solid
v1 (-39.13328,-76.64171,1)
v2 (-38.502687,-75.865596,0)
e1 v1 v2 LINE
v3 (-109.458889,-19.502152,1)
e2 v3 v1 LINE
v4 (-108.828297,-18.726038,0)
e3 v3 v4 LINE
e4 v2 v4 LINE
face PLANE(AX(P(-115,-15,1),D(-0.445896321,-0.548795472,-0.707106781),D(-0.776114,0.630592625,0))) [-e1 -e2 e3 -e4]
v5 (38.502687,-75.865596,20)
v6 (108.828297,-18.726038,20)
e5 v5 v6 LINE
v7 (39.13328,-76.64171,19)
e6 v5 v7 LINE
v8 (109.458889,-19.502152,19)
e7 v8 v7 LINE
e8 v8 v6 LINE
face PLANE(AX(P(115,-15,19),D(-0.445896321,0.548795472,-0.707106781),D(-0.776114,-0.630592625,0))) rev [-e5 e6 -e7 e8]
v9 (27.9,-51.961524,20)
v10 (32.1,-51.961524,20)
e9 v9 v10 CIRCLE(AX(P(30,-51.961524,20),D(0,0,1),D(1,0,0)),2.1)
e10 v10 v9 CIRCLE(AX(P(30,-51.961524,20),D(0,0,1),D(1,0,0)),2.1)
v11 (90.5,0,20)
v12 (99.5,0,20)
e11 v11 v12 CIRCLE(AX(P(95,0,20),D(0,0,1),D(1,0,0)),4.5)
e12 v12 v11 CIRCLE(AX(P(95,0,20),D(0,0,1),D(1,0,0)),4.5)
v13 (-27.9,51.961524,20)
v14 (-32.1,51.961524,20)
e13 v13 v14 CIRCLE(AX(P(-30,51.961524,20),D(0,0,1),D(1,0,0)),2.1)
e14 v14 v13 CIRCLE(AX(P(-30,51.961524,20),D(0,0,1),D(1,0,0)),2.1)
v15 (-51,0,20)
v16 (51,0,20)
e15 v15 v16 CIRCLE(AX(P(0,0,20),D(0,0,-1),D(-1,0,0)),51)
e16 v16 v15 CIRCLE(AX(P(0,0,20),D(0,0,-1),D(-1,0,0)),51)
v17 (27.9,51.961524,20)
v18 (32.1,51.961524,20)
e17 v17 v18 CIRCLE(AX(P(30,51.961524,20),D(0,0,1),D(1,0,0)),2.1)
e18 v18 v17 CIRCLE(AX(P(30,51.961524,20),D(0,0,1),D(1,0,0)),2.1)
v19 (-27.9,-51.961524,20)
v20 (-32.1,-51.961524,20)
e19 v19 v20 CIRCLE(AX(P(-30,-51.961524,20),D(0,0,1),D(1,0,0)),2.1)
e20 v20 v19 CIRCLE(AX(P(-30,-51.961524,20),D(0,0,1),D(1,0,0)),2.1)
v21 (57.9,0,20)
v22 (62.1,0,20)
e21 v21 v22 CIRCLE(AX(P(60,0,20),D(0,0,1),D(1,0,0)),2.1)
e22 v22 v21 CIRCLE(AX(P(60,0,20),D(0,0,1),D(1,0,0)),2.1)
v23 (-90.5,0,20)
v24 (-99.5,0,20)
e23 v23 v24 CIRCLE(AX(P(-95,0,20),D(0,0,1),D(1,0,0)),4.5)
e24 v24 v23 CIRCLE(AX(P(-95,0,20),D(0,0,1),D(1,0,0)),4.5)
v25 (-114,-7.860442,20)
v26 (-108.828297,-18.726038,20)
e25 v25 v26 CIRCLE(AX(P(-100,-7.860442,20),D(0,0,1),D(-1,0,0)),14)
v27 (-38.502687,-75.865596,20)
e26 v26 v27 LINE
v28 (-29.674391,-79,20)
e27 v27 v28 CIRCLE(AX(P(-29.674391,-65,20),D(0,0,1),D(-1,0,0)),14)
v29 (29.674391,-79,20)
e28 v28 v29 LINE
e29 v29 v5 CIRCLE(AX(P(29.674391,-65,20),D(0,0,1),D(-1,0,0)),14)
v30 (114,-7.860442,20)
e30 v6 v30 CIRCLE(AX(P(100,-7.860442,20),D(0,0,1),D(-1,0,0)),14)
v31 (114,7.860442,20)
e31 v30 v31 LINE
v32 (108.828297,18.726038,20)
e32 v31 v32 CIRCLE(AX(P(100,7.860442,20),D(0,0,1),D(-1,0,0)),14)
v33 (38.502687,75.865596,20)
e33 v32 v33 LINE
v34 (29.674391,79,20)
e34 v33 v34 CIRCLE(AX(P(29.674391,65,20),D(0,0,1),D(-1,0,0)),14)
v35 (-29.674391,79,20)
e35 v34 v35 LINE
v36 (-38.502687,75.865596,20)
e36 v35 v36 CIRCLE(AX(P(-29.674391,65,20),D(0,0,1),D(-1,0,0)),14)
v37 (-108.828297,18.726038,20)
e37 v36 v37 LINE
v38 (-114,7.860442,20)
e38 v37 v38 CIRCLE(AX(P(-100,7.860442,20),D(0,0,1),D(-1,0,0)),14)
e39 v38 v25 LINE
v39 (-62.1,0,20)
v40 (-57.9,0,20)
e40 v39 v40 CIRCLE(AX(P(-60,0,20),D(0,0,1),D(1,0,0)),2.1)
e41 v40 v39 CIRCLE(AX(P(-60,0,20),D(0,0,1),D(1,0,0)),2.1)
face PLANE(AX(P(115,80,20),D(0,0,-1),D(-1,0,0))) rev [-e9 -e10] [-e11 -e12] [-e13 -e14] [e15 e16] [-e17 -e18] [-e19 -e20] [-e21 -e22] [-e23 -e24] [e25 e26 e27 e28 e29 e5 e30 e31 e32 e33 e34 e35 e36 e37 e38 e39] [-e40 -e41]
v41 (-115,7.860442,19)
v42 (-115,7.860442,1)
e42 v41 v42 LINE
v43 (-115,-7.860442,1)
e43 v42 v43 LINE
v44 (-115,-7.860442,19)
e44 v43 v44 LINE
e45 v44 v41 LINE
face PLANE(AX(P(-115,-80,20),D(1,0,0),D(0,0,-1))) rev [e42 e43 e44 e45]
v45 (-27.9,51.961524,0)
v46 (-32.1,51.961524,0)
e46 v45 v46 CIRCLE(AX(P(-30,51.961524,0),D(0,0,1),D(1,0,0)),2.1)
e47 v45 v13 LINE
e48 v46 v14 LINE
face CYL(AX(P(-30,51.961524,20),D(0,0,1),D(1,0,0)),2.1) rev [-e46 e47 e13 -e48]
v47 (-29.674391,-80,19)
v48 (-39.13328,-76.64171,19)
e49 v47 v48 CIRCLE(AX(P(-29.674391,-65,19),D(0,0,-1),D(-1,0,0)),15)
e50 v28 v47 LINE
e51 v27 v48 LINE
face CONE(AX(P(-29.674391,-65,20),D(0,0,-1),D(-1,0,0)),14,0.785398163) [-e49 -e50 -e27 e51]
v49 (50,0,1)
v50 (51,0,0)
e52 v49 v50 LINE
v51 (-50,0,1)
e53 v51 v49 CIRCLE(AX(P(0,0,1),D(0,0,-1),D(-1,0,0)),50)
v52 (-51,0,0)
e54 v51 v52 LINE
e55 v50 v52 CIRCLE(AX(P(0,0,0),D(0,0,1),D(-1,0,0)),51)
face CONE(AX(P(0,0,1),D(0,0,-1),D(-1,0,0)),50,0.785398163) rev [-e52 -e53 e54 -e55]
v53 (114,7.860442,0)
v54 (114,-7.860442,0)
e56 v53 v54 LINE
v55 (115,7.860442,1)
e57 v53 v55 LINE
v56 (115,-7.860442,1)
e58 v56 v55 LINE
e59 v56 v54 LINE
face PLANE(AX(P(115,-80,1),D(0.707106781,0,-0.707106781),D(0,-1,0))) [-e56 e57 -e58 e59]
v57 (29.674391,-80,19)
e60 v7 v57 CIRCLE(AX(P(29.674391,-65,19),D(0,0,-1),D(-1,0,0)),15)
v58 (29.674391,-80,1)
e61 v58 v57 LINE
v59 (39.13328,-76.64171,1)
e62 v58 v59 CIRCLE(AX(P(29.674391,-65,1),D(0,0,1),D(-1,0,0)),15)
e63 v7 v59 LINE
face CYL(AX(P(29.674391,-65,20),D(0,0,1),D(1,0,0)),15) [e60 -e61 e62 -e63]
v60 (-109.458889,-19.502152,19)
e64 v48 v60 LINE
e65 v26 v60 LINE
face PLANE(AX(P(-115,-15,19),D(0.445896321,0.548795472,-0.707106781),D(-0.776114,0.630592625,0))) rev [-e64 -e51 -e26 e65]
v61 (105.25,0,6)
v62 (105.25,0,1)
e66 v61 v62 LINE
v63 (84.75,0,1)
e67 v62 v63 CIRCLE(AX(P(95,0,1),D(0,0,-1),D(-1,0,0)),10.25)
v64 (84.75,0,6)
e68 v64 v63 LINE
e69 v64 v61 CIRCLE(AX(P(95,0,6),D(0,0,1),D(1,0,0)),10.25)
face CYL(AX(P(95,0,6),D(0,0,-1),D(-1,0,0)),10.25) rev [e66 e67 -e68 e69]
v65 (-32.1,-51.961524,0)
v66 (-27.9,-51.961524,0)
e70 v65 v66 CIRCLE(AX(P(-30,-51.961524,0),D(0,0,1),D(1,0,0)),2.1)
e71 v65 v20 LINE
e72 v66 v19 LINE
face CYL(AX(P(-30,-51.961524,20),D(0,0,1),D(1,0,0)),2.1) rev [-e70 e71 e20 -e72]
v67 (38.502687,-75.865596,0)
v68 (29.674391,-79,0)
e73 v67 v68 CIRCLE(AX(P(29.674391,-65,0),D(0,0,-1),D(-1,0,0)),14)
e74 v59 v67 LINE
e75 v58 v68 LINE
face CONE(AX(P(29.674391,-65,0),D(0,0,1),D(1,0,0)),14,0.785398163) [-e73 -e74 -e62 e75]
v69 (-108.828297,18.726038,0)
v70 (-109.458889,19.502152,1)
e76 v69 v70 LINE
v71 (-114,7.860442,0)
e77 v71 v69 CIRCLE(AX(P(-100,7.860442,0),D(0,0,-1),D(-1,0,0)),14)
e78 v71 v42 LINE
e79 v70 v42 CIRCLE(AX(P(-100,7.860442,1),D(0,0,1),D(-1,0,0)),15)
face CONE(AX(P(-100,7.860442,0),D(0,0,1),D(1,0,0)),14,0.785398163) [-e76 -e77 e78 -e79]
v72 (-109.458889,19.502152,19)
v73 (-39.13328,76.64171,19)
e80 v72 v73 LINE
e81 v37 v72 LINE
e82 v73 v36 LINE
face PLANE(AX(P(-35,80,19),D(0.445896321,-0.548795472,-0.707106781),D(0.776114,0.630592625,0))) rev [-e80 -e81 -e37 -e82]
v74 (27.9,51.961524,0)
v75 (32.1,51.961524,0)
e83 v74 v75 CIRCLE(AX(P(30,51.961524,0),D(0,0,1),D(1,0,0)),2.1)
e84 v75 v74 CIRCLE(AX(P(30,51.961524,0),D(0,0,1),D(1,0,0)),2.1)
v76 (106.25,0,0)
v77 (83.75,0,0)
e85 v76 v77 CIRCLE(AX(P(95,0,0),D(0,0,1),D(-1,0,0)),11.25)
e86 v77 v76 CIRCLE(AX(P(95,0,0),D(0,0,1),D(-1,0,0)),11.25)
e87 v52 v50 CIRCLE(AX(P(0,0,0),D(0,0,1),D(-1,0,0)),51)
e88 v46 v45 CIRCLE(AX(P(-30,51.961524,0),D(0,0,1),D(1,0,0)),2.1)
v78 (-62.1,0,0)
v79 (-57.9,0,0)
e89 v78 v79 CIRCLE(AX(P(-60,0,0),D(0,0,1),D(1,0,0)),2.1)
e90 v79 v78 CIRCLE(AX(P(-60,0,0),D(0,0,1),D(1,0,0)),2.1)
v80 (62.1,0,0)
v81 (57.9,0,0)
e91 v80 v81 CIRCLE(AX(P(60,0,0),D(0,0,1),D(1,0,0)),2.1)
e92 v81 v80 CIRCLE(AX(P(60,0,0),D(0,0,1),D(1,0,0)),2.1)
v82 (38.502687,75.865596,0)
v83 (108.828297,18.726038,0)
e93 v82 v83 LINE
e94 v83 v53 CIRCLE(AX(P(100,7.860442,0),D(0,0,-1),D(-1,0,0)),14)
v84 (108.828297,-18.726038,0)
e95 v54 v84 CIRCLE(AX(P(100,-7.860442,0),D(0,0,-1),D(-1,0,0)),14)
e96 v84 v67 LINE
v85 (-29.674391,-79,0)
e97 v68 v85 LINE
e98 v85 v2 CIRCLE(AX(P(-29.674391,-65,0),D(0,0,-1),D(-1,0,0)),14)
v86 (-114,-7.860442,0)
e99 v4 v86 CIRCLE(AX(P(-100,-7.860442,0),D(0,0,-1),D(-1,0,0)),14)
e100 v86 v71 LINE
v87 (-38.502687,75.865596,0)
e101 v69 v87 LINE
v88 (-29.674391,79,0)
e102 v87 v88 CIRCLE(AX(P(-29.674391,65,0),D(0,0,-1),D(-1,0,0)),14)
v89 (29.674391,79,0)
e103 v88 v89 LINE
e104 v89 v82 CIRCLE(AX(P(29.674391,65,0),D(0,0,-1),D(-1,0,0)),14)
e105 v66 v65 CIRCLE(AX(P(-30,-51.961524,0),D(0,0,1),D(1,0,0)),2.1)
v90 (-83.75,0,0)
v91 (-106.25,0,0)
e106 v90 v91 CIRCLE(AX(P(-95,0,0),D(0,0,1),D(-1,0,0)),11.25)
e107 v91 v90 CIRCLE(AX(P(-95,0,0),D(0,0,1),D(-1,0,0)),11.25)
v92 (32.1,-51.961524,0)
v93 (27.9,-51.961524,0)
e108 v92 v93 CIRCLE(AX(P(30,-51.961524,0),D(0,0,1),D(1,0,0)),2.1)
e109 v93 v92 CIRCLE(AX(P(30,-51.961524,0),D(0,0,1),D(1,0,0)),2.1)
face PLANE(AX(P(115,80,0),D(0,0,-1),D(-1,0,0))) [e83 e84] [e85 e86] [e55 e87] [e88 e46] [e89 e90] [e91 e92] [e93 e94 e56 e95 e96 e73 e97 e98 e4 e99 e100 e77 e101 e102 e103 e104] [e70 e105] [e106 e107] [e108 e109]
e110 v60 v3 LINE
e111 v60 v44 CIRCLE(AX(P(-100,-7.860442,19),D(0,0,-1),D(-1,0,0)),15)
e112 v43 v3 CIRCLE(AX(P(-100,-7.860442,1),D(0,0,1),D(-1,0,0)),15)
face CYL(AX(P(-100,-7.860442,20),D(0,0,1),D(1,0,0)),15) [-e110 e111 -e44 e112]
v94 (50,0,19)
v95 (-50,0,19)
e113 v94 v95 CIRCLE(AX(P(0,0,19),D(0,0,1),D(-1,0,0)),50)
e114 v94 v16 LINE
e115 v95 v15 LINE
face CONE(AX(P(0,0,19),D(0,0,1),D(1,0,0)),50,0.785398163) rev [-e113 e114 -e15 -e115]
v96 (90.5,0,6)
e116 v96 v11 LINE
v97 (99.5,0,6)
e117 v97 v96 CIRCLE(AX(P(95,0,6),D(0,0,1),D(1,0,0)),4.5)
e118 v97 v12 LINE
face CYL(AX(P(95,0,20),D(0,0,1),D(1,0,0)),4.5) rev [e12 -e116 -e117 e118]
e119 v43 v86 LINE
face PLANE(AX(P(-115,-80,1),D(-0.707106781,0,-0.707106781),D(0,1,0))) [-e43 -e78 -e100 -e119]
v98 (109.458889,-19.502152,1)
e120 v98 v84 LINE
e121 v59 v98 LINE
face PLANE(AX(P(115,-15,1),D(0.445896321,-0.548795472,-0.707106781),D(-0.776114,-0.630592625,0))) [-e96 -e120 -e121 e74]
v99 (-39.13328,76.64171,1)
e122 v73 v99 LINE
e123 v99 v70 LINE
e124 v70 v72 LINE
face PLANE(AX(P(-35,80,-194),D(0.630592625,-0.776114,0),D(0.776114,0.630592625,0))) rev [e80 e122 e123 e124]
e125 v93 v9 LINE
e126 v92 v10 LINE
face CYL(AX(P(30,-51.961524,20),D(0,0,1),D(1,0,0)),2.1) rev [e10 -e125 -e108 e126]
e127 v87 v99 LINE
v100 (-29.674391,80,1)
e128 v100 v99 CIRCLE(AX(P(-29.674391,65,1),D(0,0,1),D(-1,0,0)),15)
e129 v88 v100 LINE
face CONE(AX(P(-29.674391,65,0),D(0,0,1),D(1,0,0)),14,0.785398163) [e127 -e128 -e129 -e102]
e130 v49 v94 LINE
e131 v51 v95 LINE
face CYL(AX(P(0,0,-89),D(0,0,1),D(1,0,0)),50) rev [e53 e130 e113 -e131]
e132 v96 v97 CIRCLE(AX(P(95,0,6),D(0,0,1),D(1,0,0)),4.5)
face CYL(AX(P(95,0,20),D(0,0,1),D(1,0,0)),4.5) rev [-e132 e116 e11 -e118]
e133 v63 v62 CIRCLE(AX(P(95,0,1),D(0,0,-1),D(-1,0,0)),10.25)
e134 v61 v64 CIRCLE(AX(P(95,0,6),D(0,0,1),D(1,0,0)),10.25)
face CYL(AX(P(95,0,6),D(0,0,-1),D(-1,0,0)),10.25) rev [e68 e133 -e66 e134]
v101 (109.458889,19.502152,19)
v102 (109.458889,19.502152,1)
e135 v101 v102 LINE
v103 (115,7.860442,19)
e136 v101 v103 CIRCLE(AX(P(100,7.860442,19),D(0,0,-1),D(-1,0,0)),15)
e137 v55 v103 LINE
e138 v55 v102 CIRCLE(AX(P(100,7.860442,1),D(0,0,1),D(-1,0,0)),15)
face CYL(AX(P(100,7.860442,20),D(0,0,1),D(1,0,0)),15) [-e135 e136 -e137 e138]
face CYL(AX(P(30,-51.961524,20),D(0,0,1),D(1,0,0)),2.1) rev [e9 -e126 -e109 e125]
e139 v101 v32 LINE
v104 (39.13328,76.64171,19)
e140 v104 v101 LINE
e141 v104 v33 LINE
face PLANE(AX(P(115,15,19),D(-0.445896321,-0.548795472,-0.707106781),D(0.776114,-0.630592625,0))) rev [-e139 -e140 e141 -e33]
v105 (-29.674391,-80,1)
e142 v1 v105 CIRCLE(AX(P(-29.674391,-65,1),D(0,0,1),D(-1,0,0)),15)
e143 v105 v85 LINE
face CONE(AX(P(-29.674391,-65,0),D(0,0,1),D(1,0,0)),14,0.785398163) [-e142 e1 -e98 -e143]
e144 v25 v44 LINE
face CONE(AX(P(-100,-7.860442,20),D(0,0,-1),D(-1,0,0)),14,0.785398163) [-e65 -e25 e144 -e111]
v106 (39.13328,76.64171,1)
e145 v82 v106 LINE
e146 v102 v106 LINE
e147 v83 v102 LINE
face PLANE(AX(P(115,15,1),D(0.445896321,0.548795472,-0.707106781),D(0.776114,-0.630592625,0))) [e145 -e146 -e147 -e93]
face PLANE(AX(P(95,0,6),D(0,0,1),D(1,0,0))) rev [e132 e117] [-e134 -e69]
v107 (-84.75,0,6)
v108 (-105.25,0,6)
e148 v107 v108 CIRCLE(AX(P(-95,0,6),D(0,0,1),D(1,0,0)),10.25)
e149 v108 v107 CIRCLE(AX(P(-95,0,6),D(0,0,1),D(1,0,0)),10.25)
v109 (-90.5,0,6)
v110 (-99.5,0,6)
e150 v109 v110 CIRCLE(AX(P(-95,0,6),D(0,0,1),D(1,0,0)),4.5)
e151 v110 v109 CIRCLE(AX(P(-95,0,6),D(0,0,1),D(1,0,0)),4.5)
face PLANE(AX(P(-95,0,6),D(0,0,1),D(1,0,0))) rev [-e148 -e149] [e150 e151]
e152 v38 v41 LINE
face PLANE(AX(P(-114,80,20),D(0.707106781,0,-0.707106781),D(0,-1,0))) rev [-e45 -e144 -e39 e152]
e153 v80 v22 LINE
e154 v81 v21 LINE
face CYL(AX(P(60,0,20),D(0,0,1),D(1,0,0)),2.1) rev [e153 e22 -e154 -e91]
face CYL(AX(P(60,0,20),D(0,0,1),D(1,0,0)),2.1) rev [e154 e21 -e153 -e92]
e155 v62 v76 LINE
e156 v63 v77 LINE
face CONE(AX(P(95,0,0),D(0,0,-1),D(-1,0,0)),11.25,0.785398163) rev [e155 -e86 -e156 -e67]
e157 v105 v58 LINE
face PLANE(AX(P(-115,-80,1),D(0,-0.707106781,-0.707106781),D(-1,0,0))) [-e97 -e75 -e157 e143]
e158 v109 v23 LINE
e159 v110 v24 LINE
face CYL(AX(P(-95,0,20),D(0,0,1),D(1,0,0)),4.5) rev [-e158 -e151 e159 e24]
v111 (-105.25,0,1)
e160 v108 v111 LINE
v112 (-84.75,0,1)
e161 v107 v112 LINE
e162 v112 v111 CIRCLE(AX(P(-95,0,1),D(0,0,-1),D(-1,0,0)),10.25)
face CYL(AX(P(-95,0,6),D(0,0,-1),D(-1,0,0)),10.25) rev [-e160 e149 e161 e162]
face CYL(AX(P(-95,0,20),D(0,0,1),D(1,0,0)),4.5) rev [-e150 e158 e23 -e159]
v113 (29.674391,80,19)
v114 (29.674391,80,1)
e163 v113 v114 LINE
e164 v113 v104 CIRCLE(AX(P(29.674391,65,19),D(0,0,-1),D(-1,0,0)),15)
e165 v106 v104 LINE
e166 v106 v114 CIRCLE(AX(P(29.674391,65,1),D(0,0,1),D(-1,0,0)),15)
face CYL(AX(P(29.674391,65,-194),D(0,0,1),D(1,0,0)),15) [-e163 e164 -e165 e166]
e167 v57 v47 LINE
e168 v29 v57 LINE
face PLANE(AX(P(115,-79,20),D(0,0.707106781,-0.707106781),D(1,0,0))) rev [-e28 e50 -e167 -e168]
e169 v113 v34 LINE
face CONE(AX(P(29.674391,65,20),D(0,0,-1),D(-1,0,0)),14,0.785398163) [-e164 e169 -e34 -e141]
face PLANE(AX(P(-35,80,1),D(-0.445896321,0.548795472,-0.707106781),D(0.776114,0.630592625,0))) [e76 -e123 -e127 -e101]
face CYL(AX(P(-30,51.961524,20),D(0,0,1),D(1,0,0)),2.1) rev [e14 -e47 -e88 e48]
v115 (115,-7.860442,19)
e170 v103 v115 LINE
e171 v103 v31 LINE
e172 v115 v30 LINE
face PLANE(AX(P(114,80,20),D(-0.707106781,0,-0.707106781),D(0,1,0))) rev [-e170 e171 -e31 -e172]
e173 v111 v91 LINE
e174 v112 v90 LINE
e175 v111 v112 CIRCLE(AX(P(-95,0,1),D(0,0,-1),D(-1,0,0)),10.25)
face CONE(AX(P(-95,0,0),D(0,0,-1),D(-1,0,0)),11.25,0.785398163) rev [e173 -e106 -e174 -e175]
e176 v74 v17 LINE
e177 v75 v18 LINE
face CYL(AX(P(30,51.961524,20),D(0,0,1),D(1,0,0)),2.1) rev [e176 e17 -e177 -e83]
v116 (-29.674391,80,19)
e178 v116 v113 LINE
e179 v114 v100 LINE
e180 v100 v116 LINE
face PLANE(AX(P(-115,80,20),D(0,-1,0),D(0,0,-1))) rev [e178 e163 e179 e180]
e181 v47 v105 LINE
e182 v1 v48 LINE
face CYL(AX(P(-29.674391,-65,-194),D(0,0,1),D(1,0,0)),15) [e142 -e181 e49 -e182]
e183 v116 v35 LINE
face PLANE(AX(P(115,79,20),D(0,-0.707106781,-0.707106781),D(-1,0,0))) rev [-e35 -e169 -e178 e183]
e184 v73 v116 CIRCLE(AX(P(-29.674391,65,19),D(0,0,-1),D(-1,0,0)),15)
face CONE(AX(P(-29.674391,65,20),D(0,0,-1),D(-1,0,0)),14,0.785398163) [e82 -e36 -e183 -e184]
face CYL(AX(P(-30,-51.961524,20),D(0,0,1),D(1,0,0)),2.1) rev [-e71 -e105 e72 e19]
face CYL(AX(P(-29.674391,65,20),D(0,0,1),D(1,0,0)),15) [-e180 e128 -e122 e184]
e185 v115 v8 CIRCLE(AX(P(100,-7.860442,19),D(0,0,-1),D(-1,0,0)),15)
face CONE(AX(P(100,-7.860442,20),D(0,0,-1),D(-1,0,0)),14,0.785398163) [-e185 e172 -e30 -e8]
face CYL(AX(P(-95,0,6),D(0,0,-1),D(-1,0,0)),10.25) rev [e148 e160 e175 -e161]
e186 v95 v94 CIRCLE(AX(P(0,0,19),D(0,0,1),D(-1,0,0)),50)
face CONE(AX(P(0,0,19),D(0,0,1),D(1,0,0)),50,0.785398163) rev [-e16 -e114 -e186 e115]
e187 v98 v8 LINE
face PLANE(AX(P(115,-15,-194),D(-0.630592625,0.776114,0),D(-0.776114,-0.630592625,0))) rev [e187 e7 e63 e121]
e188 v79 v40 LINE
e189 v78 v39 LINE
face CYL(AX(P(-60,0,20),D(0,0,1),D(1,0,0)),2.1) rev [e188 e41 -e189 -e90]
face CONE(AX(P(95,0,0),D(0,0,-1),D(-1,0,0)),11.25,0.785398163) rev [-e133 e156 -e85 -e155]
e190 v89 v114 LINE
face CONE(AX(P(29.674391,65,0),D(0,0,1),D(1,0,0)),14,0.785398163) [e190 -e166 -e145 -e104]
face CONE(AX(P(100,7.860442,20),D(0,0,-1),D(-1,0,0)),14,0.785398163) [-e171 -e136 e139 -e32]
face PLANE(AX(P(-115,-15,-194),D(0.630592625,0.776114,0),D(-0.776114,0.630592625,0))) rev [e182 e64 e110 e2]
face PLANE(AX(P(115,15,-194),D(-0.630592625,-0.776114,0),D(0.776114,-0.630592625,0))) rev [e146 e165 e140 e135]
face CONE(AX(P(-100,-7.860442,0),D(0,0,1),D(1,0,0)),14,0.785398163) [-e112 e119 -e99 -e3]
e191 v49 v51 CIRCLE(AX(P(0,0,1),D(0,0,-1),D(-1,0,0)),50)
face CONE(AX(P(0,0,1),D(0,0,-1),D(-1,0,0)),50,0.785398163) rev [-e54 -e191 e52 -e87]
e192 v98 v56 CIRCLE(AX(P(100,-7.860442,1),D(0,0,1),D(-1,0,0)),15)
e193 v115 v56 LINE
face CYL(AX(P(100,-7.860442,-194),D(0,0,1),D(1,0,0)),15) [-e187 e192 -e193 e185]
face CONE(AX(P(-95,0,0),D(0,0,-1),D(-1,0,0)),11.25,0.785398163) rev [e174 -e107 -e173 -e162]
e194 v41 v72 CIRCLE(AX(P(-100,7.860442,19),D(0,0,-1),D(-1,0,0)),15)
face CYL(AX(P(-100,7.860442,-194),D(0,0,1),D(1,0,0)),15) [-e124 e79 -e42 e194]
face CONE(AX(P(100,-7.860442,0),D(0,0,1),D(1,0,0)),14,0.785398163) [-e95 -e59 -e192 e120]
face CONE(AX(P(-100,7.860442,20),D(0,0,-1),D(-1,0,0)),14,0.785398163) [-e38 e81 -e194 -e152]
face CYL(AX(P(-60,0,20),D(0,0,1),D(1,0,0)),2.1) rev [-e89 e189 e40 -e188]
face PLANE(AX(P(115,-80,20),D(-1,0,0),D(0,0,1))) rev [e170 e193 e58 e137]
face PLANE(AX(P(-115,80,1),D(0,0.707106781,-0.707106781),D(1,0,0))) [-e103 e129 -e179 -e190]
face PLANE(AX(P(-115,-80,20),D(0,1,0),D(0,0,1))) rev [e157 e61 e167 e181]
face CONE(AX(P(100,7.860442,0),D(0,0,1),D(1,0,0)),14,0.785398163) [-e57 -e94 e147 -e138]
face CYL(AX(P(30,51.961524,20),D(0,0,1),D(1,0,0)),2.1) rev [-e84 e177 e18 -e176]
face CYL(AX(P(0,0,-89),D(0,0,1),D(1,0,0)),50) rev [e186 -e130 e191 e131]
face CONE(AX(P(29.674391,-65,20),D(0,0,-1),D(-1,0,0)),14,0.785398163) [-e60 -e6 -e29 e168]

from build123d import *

# Parameters (mm, degrees)
SKETCH1_W            = 230
SKETCH1_H            = 160
BOSS_EXTRUDE1_DEPTH  = 20
SKETCH4_R            = 50
CUT_EXTRUDE3_DEPTH   = 109
SKETCH5_R            = 10.25
CUT_EXTRUDE4_DEPTH   = 6
M8_CLEARANCE_HOLE1_D = 9
CHAMFER2_SIZE        = 1
CUT_EXTRUDE6_DEPTH   = 214
FILLET1_R            = 15
CHAMFER3_SIZE        = 1
CHAMFER4_SIZE        = 1
M5_TAPPED_HOLE1_D    = 4.2


with BuildPart() as part:
    # Sketch1 → Boss-Extrude1 (new body)
    with BuildSketch(Plane.XY):
        Rectangle(SKETCH1_W, SKETCH1_H)
    extrude(amount=BOSS_EXTRUDE1_DEPTH)

    # Sketch4 → Cut-Extrude3 (cut)
    with BuildSketch(Plane.XY.offset(20)):
        Circle(SKETCH4_R)
    extrude(amount=-CUT_EXTRUDE3_DEPTH, mode=Mode.SUBTRACT)

    # Sketch5 → Cut-Extrude4 (cut)
    with BuildSketch(Plane.XY):
        with Locations((-95, 0)):
            Circle(SKETCH5_R)
        with Locations((95, 0)):
            Circle(SKETCH5_R)
    extrude(amount=CUT_EXTRUDE4_DEPTH, mode=Mode.SUBTRACT)

    # M8 Clearance Hole1 (through all)
    with Locations(Plane.XY.offset(20)):
        with Locations((-95, 0), (95, 0)):
            Hole(M8_CLEARANCE_HOLE1_D / 2)

    # Chamfer2
    chamfer2_edges = [part.edges().sort_by_distance(p)[0] for p in [
        (-50, 0, 0),
        (-50, 0, 20),
    ]]
    chamfer(chamfer2_edges, length=CHAMFER2_SIZE)

    # Sketch10 → Cut-Extrude6 (cut)
    with BuildSketch(Plane.XY.offset(20)):
        Polygon((-115, 80), (-35, 80), (-115, 15), align=None)
        Polygon((35, 80), (115, 80), (115, 15), align=None)
        Polygon((-115, -15), (-35, -80), (-115, -80), align=None)
        Polygon((35, -80), (115, -80), (115, -15), align=None)
    extrude(amount=-CUT_EXTRUDE6_DEPTH, mode=Mode.SUBTRACT)

    # Fillet1
    fillet1_edges = [part.edges().sort_by_distance(p)[0] for p in [
        (115, 15, 10),
        (35, 80, 10),
        (-115, -15, 10),
        (-35, -80, 10),
        (35, -80, 10),
        (115, -15, 10),
        (-115, 15, 10),
        (-35, 80, 10),
    ]]
    fillet(fillet1_edges, radius=FILLET1_R)

    # Chamfer3
    chamfer3_edges = [part.edges().sort_by_distance(p)[0] for p in [
        (-74.296084687, 48.071931192, 0),
        (-74.296084687, 48.071931192, 20),
        (115, 0, 20),
        (74.296084687, 48.071931192, 20),
        (0, 80, 20),
        (-115, 0, 20),
        (-74.296084687, -48.071931192, 20),
        (0, -80, 20),
        (74.296084687, -48.071931192, 20),
        (-113.544064025, -14.307017415, 20),
        (-34.693073216, -79.13551644, 20),
        (34.693073216, -79.13551644, 20),
        (113.544064025, -14.307017415, 20),
        (113.544064025, 14.307017415, 20),
        (34.693073216, 79.13551644, 20),
        (-34.693073216, 79.13551644, 20),
        (-113.544064025, 14.307017415, 20),
        (-115, 0, 0),
        (74.296084687, 48.071931192, 0),
        (115, 0, 0),
        (74.296084687, -48.071931192, 0),
        (0, -80, 0),
        (-74.296084687, -48.071931192, 0),
        (0, 80, 0),
        (-113.544064025, -14.307017415, 0),
        (-34.693073216, -79.13551644, 0),
        (34.693073216, -79.13551644, 0),
        (113.544064025, -14.307017415, 0),
        (113.544064025, 14.307017415, 0),
        (34.693073216, 79.13551644, 0),
        (-34.693073216, 79.13551644, 0),
        (-113.544064025, 14.307017415, 0),
    ]]
    chamfer(chamfer3_edges, length=CHAMFER3_SIZE)

    # Chamfer4
    chamfer4_edges = [part.edges().sort_by_distance(p)[0] for p in [
        (-105.25, 0, 0),
        (84.75, 0, 0),
    ]]
    chamfer(chamfer4_edges, length=CHAMFER4_SIZE)

    # M5 Tapped Hole1 (through all)
    with Locations(Plane.XY.offset(20)):
        with Locations((-30, 51.961524227), (-60, 0), (-30, -51.961524227), (30, -51.961524227), (60, 0), (30, 51.961524227)):
            Hole(M5_TAPPED_HOLE1_D / 2)


solid = part.part
